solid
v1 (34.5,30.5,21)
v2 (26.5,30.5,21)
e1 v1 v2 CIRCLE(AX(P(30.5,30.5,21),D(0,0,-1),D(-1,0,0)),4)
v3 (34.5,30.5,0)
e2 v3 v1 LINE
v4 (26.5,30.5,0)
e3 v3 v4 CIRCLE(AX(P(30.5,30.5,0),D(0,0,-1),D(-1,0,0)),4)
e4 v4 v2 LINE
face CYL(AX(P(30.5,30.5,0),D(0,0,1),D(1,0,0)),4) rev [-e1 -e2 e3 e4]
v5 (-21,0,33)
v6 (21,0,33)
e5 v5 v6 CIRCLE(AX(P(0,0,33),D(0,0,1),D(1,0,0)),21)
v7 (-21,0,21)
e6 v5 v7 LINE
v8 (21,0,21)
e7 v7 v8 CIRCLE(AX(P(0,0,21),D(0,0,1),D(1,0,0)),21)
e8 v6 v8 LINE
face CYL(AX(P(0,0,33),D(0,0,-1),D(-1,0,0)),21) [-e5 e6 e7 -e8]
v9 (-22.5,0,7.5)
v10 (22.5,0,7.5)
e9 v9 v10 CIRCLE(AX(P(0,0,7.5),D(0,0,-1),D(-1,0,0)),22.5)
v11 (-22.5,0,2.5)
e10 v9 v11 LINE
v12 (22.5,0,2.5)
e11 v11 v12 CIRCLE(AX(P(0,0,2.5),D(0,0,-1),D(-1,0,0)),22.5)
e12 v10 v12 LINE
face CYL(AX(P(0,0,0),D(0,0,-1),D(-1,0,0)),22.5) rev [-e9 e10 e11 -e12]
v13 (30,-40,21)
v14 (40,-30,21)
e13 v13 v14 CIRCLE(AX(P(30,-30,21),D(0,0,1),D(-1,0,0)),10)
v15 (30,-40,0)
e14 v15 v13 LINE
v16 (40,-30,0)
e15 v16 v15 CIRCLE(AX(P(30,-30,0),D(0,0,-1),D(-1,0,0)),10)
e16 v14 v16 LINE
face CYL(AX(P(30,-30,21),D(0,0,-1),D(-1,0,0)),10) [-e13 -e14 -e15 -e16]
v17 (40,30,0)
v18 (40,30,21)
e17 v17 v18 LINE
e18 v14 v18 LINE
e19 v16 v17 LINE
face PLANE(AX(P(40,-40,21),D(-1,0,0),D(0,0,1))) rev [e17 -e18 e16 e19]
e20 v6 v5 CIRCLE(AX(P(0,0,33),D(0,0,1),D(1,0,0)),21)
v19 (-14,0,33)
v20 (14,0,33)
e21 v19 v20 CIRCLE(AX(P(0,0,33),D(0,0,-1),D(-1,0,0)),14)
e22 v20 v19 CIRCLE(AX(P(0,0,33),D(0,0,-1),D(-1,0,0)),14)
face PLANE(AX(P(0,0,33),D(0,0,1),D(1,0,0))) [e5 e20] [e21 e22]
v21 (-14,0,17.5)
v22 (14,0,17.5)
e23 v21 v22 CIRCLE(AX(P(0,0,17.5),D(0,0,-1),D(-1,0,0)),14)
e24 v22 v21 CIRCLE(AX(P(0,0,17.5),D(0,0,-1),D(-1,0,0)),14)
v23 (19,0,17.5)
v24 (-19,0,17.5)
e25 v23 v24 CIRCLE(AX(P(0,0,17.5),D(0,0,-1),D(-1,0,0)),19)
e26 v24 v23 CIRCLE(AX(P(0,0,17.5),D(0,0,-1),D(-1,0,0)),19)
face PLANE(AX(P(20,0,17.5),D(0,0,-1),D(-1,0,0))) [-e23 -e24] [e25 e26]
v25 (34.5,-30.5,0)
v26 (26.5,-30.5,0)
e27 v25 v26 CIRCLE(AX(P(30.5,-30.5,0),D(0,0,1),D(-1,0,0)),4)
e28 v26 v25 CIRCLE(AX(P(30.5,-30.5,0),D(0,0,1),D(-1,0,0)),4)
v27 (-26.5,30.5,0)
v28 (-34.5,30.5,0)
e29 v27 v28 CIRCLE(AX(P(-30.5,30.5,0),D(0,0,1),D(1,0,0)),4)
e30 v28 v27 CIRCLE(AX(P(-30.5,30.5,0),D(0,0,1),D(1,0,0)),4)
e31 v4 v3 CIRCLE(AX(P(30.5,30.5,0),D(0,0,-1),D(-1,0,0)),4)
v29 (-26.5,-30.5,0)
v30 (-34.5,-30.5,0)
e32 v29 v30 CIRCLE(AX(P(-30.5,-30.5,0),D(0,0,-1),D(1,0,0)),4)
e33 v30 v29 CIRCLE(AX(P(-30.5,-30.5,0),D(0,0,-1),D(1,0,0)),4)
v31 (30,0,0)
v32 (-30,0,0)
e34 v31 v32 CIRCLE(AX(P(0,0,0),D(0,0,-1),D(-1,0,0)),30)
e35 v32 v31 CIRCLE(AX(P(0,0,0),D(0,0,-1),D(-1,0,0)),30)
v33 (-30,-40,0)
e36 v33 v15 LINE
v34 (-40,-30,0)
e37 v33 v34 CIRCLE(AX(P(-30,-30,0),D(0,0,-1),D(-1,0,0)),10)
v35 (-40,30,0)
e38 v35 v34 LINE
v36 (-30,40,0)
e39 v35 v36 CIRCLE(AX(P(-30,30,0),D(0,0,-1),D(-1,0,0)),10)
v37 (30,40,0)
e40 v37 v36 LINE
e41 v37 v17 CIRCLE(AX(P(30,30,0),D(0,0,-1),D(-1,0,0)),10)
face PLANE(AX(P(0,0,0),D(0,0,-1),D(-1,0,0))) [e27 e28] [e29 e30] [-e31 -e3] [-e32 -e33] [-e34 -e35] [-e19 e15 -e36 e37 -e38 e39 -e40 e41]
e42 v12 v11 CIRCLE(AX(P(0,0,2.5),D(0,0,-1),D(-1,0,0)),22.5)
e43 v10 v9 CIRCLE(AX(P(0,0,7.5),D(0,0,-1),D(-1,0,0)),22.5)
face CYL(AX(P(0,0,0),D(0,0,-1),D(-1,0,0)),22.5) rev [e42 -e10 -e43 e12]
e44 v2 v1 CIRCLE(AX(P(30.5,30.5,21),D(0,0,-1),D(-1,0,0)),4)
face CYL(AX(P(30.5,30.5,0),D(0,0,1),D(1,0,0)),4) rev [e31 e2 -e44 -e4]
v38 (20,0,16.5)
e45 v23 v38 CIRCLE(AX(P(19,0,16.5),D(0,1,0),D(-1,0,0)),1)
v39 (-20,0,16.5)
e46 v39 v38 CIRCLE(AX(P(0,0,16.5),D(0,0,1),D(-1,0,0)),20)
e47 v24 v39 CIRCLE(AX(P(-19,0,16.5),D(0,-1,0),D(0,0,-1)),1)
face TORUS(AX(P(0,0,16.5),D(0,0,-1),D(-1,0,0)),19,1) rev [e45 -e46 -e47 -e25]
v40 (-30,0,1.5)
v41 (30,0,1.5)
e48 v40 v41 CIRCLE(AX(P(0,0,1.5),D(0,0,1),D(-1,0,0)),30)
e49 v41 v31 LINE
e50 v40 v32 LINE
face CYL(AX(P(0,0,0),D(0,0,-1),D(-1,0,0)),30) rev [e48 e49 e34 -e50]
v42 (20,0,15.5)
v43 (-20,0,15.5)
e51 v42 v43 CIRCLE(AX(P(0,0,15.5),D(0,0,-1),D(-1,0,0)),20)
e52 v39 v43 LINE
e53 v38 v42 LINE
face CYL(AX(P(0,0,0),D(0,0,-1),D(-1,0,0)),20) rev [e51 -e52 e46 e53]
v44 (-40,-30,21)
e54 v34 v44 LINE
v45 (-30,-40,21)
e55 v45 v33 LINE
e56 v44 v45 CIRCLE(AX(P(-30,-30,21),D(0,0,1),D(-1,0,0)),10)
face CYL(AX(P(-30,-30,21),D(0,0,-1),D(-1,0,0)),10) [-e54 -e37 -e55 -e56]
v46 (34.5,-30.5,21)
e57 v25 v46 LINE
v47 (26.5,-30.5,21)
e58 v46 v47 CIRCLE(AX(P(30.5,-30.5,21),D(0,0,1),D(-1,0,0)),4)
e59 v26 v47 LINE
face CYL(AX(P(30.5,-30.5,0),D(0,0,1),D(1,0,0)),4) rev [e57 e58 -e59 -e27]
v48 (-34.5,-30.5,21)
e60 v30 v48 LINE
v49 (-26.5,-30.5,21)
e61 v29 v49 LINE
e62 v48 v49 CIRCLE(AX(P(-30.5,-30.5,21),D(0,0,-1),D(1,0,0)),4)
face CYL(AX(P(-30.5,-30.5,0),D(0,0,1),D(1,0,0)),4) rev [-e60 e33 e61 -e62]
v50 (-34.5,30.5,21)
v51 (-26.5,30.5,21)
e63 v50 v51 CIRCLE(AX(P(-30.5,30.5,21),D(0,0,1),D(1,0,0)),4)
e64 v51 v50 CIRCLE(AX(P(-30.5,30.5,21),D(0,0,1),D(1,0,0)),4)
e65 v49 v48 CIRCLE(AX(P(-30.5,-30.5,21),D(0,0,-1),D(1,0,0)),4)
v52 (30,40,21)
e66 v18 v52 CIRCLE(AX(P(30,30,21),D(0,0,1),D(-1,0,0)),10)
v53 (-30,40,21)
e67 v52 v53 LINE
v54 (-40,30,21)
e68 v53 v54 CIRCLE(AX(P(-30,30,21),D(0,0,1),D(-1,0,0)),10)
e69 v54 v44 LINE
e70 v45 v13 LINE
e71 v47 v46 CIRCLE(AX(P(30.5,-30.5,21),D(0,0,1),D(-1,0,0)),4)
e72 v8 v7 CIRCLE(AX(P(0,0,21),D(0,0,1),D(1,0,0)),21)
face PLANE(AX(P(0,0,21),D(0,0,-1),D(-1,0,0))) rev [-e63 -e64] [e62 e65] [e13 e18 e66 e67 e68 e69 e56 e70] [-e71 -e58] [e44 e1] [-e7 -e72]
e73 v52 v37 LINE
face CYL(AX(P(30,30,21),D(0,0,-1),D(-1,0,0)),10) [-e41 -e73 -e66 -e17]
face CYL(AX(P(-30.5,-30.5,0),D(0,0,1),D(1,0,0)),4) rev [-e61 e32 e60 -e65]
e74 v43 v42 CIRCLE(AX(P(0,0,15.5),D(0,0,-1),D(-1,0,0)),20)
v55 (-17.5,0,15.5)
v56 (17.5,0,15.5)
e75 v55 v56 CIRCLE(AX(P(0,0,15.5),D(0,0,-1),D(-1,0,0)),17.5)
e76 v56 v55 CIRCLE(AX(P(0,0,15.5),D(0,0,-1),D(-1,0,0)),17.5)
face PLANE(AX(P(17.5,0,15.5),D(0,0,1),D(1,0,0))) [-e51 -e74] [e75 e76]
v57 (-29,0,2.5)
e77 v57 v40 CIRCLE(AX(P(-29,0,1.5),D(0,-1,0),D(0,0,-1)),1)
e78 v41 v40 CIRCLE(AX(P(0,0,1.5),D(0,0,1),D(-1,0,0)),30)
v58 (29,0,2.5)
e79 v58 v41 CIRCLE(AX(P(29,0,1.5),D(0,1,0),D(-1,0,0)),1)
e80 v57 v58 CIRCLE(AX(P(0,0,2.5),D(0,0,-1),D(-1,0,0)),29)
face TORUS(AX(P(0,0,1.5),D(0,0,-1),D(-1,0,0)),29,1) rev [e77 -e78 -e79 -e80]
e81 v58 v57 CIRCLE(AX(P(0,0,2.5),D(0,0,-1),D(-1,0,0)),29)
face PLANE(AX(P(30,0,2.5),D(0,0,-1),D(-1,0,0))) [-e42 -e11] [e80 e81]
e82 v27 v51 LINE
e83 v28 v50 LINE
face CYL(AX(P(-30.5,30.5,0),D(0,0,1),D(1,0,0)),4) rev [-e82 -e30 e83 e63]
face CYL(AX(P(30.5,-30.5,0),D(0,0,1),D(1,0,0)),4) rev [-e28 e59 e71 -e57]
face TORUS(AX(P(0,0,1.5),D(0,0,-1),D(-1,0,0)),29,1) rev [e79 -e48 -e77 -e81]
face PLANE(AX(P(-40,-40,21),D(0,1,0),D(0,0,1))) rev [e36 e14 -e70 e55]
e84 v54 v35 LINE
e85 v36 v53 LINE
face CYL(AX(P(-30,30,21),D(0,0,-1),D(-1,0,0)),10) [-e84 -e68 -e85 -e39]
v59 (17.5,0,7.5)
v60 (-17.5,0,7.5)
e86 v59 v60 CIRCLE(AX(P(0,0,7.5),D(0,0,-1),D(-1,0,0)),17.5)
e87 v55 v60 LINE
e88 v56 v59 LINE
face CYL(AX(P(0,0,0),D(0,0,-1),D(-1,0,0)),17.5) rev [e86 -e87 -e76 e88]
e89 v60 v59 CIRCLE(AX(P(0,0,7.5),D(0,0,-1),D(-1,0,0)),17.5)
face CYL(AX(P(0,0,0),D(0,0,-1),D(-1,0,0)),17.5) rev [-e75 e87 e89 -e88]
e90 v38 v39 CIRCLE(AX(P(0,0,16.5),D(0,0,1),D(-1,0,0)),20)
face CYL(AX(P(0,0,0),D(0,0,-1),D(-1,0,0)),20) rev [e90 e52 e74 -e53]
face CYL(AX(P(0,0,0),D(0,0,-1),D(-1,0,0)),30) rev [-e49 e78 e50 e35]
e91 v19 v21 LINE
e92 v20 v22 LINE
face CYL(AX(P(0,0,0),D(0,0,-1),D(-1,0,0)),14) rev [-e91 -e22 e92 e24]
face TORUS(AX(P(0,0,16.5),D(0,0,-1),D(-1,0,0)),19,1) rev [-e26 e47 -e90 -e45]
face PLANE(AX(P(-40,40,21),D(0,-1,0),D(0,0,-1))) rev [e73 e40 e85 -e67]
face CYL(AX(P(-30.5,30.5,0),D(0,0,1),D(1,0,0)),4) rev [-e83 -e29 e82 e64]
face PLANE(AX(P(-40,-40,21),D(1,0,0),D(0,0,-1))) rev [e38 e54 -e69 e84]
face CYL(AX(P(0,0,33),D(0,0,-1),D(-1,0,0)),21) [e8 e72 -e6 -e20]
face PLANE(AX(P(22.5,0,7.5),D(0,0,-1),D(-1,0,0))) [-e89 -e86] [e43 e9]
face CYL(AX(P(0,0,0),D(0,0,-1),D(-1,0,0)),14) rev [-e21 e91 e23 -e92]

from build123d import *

# Parameters (mm, degrees)
SKETCH_1_W               = 80
SKETCH_1_H               = 80
EXTRUDE_1_DEPTH          = 21
SKETCH_2_R               = 21
EXTRUDE_2_DEPTH          = 12
FILLET_1_R               = 10
SKETCH_6_R               = 4
CUT_EXTRUDE_1_DEPTH      = 21
MIRROR_2_COPY_1_SKETCH_R = 4
MIRROR_2_COPY_1_DEPTH    = 21
FILLET_2_R               = 1
FILLET_3_R               = 1


with BuildPart() as part:
    # 草图1 → 凸台-拉伸1 (new body)
    with BuildSketch(Plane.XY):
        Rectangle(SKETCH_1_W, SKETCH_1_H)
    extrude(amount=EXTRUDE_1_DEPTH)

    # 草图2 → 凸台-拉伸2 (add)
    with BuildSketch(Plane.XY.offset(21)):
        Circle(SKETCH_2_R)
    extrude(amount=EXTRUDE_2_DEPTH)

    # 草图3 → 切除-旋转1 (revolve, cut)
    with BuildSketch(Plane(origin=(0, 0, 0), x_dir=(1, 0, 0), z_dir=(0, 1, 0)), mode=Mode.PRIVATE) as cut_revolve_1_sk:
        Polygon((30, 0), (30, -2.5), (22.5, -2.5), (22.5, -7.5), (17.5, -7.5), (17.5, -15.5), (20, -15.5), (20, -17.5), (14, -17.5), (14, -33), (0, -33), (0, 0), align=None)
    revolve(cut_revolve_1_sk.sketch.rotate(Axis((0, 0, 0), (0, 0, 1)), 180), axis=Axis((0, 0, 0), (0, 0, 1)), mode=Mode.SUBTRACT)

    # 圆角1
    fillet_1_edges = [part.edges().sort_by_distance(p)[0] for p in [
        (40, -40, 10.5),
        (-40, -40, 10.5),
        (-40, 40, 10.5),
        (40, 40, 10.5),
    ]]
    fillet(fillet_1_edges, radius=FILLET_1_R)

    # 草图6 → 切除-拉伸1 (cut)
    with BuildSketch(Plane.XY.offset(21)):
        with Locations((-30.5, 30.5)):
            Circle(SKETCH_6_R)
    cut_extrude_1 = extrude(amount=-CUT_EXTRUDE_1_DEPTH, mode=Mode.SUBTRACT)

    # 镜向1: 切除-拉伸1 across plane
    add(cut_extrude_1.mirror(Plane.ZX), mode=Mode.SUBTRACT)

    # 镜向2: 切除-拉伸1 across plane
    add(cut_extrude_1.mirror(Plane(origin=(0, 0, 0), x_dir=(0, 0, 1), z_dir=(1, 0, 0))), mode=Mode.SUBTRACT)

    # 镜向2 copy 1 sketch → 镜向2 copy 1 (cut)
    with BuildSketch(Plane(origin=(0, 0, 21), x_dir=(-1, 0, 0), z_dir=(0, 0, 1))):
        with Locations((-30.5, 30.5)):
            Circle(MIRROR_2_COPY_1_SKETCH_R)
    extrude(amount=-MIRROR_2_COPY_1_DEPTH, mode=Mode.SUBTRACT)

    # 圆角2
    fillet_2_edges = [part.edges().sort_by_distance(p)[0] for p in [
        (30, 0, 2.5),
    ]]
    fillet(fillet_2_edges, radius=FILLET_2_R)

    # 圆角3
    fillet_3_edges = [part.edges().sort_by_distance(p)[0] for p in [
        (20, 0, 17.5),
    ]]
    fillet(fillet_3_edges, radius=FILLET_3_R)


solid = part.part
